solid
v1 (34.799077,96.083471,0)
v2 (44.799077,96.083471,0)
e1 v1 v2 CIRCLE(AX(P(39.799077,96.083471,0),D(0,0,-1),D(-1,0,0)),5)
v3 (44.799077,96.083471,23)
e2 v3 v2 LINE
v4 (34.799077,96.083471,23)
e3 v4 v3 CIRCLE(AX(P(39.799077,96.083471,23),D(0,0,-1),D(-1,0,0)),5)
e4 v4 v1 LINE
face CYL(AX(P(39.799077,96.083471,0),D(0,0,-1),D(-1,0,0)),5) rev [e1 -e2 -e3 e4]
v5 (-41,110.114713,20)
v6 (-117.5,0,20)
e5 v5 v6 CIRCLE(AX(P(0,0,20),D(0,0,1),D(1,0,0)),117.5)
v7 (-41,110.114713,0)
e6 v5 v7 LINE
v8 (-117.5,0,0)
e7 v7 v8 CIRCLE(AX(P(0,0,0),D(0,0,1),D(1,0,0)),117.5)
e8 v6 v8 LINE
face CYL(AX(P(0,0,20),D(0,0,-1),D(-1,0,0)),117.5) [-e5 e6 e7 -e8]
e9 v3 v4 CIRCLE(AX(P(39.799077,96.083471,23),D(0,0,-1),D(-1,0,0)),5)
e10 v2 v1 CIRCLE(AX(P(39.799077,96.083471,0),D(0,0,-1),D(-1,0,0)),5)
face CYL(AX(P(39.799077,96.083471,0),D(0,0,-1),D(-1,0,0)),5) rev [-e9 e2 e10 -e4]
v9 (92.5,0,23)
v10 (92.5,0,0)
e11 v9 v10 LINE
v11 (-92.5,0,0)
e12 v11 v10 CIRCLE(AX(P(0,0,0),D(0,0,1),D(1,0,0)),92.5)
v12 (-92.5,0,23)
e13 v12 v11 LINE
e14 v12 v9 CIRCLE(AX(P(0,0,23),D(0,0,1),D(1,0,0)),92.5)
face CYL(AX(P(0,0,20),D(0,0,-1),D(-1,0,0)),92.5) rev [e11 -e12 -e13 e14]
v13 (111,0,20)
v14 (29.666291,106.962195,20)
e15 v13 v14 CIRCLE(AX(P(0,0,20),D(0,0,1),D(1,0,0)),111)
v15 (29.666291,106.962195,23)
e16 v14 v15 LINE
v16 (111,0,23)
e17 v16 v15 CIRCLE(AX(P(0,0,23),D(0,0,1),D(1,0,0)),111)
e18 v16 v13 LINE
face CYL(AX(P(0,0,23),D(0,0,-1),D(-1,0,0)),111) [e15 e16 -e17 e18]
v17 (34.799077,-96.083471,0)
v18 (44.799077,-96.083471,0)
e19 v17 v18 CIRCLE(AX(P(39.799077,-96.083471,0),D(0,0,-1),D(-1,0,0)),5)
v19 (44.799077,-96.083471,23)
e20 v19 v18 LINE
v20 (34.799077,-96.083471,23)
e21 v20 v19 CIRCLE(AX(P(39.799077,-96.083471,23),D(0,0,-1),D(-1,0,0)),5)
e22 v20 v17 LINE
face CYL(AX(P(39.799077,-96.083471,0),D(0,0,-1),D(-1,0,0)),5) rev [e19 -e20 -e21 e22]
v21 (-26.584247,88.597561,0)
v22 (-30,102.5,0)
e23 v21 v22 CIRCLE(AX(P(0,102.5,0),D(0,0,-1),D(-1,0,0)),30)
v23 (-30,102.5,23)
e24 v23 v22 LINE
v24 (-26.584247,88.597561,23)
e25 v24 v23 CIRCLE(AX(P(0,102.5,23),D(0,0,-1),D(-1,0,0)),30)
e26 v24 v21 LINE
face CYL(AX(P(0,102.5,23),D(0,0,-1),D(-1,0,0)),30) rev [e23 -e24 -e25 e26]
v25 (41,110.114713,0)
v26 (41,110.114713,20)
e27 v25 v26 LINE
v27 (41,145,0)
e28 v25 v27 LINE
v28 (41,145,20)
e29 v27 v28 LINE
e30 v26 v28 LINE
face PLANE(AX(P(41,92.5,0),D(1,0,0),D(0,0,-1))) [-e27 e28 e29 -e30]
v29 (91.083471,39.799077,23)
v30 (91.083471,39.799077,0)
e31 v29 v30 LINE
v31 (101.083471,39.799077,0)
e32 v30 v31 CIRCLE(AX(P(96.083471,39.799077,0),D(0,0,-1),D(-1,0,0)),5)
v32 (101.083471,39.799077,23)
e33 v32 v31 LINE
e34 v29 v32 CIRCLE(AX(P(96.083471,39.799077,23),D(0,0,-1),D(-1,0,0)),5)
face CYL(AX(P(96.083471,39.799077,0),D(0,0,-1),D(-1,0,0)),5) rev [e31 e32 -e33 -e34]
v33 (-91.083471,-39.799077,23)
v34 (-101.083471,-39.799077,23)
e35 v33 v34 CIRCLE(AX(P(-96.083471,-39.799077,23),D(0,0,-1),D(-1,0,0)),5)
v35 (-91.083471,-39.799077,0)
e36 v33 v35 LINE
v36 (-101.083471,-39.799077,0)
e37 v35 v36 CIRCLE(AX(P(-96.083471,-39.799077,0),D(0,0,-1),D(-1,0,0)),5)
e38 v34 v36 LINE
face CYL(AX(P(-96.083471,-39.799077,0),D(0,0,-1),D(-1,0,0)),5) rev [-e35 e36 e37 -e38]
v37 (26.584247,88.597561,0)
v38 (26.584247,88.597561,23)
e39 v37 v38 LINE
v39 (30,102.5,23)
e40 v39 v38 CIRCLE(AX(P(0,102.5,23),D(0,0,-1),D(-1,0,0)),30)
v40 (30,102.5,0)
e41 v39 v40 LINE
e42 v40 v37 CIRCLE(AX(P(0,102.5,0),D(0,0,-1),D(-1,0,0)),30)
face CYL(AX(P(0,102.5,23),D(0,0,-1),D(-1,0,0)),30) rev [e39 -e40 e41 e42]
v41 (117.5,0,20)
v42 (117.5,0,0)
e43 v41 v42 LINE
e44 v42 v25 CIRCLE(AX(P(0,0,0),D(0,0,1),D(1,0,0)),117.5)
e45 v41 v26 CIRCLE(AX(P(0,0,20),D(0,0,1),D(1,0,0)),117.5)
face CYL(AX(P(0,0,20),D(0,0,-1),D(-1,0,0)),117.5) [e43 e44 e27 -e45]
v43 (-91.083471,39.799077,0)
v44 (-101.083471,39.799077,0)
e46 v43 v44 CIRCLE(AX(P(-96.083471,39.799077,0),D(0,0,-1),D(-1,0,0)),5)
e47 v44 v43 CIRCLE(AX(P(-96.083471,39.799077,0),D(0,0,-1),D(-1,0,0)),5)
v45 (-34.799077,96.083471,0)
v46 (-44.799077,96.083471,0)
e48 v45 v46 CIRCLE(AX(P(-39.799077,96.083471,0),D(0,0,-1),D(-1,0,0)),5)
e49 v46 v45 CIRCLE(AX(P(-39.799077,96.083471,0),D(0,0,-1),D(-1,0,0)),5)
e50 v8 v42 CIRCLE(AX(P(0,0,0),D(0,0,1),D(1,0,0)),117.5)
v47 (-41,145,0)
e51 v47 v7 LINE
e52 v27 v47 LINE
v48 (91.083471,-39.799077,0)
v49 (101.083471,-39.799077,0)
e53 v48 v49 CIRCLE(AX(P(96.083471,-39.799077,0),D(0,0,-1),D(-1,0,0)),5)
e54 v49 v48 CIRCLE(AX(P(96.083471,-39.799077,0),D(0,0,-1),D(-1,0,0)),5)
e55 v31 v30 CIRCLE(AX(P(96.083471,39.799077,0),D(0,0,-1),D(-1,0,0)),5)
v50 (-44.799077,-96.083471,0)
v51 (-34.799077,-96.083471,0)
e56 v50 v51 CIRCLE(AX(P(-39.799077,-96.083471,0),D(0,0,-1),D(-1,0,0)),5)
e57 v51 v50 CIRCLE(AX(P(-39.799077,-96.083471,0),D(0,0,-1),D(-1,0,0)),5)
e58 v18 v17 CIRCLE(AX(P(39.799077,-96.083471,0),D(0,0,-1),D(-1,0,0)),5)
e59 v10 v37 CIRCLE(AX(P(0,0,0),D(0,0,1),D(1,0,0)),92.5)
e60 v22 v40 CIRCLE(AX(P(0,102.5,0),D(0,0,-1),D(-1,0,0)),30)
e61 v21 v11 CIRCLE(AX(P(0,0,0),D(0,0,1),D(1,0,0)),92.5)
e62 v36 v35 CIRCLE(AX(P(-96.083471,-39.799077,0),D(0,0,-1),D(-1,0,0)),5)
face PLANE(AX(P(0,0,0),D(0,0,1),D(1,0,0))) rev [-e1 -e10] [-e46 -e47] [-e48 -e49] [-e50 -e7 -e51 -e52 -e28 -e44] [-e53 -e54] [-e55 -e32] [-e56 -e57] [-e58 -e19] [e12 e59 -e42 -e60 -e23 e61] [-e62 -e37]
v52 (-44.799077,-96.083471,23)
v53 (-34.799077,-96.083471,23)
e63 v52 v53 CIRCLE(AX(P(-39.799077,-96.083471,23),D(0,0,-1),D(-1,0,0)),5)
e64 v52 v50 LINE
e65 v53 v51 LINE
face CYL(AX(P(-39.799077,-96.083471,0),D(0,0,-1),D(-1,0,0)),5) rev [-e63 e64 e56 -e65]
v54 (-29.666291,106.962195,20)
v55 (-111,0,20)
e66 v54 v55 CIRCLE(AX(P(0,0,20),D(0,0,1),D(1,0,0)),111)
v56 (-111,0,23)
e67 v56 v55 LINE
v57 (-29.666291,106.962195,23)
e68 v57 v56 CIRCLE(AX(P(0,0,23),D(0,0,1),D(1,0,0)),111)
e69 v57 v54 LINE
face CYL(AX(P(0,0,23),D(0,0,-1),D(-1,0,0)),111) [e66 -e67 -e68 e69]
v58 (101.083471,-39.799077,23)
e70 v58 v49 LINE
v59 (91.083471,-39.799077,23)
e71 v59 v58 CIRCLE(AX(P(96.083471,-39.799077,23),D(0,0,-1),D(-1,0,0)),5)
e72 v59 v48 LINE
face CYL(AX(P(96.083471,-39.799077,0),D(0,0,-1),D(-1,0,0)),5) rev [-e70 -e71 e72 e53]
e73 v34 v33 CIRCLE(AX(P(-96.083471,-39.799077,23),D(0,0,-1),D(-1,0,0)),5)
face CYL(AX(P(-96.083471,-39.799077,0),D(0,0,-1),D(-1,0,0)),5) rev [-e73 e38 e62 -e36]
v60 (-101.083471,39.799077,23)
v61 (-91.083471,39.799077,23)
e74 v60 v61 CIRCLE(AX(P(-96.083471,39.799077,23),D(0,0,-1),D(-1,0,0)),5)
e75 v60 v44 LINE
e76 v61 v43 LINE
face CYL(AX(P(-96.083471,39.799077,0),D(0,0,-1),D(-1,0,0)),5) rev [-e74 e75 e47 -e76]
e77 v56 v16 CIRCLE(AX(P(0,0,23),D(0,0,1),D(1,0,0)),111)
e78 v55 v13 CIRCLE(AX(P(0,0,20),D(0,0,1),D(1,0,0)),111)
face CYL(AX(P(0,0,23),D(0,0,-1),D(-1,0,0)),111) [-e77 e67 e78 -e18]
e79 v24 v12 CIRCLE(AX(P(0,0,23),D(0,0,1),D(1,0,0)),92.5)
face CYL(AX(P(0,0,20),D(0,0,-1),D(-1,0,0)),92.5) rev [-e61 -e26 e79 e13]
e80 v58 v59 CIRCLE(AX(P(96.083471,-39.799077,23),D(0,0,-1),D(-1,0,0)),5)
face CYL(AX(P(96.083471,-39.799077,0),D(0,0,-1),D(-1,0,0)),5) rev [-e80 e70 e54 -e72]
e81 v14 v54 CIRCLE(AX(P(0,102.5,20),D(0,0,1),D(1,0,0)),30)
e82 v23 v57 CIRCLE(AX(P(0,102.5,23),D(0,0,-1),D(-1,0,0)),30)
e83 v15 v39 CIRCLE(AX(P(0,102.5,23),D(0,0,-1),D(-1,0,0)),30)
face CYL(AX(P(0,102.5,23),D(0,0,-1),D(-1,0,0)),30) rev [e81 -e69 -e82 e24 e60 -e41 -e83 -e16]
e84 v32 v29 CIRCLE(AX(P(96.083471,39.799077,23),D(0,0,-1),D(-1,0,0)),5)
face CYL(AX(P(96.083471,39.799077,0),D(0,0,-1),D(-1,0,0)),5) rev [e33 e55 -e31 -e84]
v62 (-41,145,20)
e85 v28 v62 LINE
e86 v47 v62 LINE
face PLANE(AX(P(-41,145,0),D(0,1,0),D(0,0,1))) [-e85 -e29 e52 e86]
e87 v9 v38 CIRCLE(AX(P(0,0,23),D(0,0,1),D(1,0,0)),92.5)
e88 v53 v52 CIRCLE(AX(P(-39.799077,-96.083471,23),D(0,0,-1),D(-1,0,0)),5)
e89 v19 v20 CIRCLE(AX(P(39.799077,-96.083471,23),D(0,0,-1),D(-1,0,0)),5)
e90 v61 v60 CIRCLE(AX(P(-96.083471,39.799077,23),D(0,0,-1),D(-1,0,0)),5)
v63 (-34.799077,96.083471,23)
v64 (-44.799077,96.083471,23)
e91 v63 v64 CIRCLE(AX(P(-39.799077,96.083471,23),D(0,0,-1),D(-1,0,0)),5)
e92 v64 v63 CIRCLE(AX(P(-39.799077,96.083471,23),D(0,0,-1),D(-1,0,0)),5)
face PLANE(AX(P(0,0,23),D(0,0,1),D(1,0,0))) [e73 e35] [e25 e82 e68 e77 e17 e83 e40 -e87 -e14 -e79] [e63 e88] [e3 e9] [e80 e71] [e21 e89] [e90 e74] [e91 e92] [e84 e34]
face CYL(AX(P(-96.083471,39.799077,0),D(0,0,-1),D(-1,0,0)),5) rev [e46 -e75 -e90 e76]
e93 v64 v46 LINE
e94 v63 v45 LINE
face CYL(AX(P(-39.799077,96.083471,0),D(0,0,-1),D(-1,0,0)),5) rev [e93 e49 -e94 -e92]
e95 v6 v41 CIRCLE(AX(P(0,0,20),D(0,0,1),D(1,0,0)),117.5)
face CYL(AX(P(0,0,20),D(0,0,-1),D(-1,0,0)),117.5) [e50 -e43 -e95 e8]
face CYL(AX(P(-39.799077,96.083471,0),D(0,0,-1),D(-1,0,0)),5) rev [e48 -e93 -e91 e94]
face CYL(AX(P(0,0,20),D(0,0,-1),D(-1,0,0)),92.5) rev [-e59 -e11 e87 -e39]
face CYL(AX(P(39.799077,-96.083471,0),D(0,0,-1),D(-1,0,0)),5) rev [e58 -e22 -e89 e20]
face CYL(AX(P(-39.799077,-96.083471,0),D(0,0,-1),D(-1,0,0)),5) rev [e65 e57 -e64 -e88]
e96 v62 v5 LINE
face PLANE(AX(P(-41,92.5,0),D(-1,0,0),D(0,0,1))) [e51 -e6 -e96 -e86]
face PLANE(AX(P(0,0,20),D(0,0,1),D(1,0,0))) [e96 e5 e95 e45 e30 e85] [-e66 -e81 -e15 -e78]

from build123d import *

# Parameters (mm, degrees)
SKETCH_1_R          = 117.5
SKETCH_1_R_2        = 92.5
EXTRUDE_1_DEPTH     = 20
SKETCH_2_W          = 82
SKETCH_2_H          = 52.5
EXTRUDE_2_DEPTH     = 20
SKETCH_7_R          = 111
SKETCH_7_R_2        = 92.5
EXTRUDE_3_DEPTH     = 3
SKETCH_3_R          = 30
CUT_EXTRUDE_1_DEPTH = 189.043213119
HOLE_WIZARD_M8_1_D  = 10


with BuildPart() as part:
    # 草图1 → 凸台-拉伸1 (new body)
    with BuildSketch(Plane.XY):
        Circle(SKETCH_1_R)
        Circle(SKETCH_1_R_2, mode=Mode.SUBTRACT)
    extrude(amount=EXTRUDE_1_DEPTH)

    # 草图2 → 凸台-拉伸2 (add, through all)
    with BuildSketch(Plane.XY.offset(20)):
        with Locations((0, 118.75)):
            Rectangle(SKETCH_2_W, SKETCH_2_H)
    extrude(amount=-EXTRUDE_2_DEPTH)

    # 草图7 → 凸台-拉伸3 (add)
    with BuildSketch(Plane.XY.offset(20)):
        Circle(SKETCH_7_R)
        Circle(SKETCH_7_R_2, mode=Mode.SUBTRACT)
    extrude(amount=EXTRUDE_3_DEPTH)

    # 草图3 → 切除-拉伸1 (cut, through all)
    with BuildSketch(Plane(origin=(0, 0, 0), x_dir=(-1, 0, 0), z_dir=(0, 0, -1))):
        with Locations((0, 102.5)):
            Circle(SKETCH_3_R)
    extrude(amount=-CUT_EXTRUDE_1_DEPTH, mode=Mode.SUBTRACT)

    # M8 间隙孔1 (through all)
    with Locations(Plane(origin=(0, 0, 0), x_dir=(-1, 0, 0), z_dir=(0, 0, -1))):
        with Locations((-39.799076966, 96.083471381), (-96.083471381, 39.799076966), (-96.083471381, -39.799076966), (-39.799076966, -96.083471381), (39.799076966, -96.083471381), (96.083471381, -39.799076966), (96.083471381, 39.799076966), (39.799076966, 96.083471381)):
            Hole(HOLE_WIZARD_M8_1_D / 2)


solid = part.part
